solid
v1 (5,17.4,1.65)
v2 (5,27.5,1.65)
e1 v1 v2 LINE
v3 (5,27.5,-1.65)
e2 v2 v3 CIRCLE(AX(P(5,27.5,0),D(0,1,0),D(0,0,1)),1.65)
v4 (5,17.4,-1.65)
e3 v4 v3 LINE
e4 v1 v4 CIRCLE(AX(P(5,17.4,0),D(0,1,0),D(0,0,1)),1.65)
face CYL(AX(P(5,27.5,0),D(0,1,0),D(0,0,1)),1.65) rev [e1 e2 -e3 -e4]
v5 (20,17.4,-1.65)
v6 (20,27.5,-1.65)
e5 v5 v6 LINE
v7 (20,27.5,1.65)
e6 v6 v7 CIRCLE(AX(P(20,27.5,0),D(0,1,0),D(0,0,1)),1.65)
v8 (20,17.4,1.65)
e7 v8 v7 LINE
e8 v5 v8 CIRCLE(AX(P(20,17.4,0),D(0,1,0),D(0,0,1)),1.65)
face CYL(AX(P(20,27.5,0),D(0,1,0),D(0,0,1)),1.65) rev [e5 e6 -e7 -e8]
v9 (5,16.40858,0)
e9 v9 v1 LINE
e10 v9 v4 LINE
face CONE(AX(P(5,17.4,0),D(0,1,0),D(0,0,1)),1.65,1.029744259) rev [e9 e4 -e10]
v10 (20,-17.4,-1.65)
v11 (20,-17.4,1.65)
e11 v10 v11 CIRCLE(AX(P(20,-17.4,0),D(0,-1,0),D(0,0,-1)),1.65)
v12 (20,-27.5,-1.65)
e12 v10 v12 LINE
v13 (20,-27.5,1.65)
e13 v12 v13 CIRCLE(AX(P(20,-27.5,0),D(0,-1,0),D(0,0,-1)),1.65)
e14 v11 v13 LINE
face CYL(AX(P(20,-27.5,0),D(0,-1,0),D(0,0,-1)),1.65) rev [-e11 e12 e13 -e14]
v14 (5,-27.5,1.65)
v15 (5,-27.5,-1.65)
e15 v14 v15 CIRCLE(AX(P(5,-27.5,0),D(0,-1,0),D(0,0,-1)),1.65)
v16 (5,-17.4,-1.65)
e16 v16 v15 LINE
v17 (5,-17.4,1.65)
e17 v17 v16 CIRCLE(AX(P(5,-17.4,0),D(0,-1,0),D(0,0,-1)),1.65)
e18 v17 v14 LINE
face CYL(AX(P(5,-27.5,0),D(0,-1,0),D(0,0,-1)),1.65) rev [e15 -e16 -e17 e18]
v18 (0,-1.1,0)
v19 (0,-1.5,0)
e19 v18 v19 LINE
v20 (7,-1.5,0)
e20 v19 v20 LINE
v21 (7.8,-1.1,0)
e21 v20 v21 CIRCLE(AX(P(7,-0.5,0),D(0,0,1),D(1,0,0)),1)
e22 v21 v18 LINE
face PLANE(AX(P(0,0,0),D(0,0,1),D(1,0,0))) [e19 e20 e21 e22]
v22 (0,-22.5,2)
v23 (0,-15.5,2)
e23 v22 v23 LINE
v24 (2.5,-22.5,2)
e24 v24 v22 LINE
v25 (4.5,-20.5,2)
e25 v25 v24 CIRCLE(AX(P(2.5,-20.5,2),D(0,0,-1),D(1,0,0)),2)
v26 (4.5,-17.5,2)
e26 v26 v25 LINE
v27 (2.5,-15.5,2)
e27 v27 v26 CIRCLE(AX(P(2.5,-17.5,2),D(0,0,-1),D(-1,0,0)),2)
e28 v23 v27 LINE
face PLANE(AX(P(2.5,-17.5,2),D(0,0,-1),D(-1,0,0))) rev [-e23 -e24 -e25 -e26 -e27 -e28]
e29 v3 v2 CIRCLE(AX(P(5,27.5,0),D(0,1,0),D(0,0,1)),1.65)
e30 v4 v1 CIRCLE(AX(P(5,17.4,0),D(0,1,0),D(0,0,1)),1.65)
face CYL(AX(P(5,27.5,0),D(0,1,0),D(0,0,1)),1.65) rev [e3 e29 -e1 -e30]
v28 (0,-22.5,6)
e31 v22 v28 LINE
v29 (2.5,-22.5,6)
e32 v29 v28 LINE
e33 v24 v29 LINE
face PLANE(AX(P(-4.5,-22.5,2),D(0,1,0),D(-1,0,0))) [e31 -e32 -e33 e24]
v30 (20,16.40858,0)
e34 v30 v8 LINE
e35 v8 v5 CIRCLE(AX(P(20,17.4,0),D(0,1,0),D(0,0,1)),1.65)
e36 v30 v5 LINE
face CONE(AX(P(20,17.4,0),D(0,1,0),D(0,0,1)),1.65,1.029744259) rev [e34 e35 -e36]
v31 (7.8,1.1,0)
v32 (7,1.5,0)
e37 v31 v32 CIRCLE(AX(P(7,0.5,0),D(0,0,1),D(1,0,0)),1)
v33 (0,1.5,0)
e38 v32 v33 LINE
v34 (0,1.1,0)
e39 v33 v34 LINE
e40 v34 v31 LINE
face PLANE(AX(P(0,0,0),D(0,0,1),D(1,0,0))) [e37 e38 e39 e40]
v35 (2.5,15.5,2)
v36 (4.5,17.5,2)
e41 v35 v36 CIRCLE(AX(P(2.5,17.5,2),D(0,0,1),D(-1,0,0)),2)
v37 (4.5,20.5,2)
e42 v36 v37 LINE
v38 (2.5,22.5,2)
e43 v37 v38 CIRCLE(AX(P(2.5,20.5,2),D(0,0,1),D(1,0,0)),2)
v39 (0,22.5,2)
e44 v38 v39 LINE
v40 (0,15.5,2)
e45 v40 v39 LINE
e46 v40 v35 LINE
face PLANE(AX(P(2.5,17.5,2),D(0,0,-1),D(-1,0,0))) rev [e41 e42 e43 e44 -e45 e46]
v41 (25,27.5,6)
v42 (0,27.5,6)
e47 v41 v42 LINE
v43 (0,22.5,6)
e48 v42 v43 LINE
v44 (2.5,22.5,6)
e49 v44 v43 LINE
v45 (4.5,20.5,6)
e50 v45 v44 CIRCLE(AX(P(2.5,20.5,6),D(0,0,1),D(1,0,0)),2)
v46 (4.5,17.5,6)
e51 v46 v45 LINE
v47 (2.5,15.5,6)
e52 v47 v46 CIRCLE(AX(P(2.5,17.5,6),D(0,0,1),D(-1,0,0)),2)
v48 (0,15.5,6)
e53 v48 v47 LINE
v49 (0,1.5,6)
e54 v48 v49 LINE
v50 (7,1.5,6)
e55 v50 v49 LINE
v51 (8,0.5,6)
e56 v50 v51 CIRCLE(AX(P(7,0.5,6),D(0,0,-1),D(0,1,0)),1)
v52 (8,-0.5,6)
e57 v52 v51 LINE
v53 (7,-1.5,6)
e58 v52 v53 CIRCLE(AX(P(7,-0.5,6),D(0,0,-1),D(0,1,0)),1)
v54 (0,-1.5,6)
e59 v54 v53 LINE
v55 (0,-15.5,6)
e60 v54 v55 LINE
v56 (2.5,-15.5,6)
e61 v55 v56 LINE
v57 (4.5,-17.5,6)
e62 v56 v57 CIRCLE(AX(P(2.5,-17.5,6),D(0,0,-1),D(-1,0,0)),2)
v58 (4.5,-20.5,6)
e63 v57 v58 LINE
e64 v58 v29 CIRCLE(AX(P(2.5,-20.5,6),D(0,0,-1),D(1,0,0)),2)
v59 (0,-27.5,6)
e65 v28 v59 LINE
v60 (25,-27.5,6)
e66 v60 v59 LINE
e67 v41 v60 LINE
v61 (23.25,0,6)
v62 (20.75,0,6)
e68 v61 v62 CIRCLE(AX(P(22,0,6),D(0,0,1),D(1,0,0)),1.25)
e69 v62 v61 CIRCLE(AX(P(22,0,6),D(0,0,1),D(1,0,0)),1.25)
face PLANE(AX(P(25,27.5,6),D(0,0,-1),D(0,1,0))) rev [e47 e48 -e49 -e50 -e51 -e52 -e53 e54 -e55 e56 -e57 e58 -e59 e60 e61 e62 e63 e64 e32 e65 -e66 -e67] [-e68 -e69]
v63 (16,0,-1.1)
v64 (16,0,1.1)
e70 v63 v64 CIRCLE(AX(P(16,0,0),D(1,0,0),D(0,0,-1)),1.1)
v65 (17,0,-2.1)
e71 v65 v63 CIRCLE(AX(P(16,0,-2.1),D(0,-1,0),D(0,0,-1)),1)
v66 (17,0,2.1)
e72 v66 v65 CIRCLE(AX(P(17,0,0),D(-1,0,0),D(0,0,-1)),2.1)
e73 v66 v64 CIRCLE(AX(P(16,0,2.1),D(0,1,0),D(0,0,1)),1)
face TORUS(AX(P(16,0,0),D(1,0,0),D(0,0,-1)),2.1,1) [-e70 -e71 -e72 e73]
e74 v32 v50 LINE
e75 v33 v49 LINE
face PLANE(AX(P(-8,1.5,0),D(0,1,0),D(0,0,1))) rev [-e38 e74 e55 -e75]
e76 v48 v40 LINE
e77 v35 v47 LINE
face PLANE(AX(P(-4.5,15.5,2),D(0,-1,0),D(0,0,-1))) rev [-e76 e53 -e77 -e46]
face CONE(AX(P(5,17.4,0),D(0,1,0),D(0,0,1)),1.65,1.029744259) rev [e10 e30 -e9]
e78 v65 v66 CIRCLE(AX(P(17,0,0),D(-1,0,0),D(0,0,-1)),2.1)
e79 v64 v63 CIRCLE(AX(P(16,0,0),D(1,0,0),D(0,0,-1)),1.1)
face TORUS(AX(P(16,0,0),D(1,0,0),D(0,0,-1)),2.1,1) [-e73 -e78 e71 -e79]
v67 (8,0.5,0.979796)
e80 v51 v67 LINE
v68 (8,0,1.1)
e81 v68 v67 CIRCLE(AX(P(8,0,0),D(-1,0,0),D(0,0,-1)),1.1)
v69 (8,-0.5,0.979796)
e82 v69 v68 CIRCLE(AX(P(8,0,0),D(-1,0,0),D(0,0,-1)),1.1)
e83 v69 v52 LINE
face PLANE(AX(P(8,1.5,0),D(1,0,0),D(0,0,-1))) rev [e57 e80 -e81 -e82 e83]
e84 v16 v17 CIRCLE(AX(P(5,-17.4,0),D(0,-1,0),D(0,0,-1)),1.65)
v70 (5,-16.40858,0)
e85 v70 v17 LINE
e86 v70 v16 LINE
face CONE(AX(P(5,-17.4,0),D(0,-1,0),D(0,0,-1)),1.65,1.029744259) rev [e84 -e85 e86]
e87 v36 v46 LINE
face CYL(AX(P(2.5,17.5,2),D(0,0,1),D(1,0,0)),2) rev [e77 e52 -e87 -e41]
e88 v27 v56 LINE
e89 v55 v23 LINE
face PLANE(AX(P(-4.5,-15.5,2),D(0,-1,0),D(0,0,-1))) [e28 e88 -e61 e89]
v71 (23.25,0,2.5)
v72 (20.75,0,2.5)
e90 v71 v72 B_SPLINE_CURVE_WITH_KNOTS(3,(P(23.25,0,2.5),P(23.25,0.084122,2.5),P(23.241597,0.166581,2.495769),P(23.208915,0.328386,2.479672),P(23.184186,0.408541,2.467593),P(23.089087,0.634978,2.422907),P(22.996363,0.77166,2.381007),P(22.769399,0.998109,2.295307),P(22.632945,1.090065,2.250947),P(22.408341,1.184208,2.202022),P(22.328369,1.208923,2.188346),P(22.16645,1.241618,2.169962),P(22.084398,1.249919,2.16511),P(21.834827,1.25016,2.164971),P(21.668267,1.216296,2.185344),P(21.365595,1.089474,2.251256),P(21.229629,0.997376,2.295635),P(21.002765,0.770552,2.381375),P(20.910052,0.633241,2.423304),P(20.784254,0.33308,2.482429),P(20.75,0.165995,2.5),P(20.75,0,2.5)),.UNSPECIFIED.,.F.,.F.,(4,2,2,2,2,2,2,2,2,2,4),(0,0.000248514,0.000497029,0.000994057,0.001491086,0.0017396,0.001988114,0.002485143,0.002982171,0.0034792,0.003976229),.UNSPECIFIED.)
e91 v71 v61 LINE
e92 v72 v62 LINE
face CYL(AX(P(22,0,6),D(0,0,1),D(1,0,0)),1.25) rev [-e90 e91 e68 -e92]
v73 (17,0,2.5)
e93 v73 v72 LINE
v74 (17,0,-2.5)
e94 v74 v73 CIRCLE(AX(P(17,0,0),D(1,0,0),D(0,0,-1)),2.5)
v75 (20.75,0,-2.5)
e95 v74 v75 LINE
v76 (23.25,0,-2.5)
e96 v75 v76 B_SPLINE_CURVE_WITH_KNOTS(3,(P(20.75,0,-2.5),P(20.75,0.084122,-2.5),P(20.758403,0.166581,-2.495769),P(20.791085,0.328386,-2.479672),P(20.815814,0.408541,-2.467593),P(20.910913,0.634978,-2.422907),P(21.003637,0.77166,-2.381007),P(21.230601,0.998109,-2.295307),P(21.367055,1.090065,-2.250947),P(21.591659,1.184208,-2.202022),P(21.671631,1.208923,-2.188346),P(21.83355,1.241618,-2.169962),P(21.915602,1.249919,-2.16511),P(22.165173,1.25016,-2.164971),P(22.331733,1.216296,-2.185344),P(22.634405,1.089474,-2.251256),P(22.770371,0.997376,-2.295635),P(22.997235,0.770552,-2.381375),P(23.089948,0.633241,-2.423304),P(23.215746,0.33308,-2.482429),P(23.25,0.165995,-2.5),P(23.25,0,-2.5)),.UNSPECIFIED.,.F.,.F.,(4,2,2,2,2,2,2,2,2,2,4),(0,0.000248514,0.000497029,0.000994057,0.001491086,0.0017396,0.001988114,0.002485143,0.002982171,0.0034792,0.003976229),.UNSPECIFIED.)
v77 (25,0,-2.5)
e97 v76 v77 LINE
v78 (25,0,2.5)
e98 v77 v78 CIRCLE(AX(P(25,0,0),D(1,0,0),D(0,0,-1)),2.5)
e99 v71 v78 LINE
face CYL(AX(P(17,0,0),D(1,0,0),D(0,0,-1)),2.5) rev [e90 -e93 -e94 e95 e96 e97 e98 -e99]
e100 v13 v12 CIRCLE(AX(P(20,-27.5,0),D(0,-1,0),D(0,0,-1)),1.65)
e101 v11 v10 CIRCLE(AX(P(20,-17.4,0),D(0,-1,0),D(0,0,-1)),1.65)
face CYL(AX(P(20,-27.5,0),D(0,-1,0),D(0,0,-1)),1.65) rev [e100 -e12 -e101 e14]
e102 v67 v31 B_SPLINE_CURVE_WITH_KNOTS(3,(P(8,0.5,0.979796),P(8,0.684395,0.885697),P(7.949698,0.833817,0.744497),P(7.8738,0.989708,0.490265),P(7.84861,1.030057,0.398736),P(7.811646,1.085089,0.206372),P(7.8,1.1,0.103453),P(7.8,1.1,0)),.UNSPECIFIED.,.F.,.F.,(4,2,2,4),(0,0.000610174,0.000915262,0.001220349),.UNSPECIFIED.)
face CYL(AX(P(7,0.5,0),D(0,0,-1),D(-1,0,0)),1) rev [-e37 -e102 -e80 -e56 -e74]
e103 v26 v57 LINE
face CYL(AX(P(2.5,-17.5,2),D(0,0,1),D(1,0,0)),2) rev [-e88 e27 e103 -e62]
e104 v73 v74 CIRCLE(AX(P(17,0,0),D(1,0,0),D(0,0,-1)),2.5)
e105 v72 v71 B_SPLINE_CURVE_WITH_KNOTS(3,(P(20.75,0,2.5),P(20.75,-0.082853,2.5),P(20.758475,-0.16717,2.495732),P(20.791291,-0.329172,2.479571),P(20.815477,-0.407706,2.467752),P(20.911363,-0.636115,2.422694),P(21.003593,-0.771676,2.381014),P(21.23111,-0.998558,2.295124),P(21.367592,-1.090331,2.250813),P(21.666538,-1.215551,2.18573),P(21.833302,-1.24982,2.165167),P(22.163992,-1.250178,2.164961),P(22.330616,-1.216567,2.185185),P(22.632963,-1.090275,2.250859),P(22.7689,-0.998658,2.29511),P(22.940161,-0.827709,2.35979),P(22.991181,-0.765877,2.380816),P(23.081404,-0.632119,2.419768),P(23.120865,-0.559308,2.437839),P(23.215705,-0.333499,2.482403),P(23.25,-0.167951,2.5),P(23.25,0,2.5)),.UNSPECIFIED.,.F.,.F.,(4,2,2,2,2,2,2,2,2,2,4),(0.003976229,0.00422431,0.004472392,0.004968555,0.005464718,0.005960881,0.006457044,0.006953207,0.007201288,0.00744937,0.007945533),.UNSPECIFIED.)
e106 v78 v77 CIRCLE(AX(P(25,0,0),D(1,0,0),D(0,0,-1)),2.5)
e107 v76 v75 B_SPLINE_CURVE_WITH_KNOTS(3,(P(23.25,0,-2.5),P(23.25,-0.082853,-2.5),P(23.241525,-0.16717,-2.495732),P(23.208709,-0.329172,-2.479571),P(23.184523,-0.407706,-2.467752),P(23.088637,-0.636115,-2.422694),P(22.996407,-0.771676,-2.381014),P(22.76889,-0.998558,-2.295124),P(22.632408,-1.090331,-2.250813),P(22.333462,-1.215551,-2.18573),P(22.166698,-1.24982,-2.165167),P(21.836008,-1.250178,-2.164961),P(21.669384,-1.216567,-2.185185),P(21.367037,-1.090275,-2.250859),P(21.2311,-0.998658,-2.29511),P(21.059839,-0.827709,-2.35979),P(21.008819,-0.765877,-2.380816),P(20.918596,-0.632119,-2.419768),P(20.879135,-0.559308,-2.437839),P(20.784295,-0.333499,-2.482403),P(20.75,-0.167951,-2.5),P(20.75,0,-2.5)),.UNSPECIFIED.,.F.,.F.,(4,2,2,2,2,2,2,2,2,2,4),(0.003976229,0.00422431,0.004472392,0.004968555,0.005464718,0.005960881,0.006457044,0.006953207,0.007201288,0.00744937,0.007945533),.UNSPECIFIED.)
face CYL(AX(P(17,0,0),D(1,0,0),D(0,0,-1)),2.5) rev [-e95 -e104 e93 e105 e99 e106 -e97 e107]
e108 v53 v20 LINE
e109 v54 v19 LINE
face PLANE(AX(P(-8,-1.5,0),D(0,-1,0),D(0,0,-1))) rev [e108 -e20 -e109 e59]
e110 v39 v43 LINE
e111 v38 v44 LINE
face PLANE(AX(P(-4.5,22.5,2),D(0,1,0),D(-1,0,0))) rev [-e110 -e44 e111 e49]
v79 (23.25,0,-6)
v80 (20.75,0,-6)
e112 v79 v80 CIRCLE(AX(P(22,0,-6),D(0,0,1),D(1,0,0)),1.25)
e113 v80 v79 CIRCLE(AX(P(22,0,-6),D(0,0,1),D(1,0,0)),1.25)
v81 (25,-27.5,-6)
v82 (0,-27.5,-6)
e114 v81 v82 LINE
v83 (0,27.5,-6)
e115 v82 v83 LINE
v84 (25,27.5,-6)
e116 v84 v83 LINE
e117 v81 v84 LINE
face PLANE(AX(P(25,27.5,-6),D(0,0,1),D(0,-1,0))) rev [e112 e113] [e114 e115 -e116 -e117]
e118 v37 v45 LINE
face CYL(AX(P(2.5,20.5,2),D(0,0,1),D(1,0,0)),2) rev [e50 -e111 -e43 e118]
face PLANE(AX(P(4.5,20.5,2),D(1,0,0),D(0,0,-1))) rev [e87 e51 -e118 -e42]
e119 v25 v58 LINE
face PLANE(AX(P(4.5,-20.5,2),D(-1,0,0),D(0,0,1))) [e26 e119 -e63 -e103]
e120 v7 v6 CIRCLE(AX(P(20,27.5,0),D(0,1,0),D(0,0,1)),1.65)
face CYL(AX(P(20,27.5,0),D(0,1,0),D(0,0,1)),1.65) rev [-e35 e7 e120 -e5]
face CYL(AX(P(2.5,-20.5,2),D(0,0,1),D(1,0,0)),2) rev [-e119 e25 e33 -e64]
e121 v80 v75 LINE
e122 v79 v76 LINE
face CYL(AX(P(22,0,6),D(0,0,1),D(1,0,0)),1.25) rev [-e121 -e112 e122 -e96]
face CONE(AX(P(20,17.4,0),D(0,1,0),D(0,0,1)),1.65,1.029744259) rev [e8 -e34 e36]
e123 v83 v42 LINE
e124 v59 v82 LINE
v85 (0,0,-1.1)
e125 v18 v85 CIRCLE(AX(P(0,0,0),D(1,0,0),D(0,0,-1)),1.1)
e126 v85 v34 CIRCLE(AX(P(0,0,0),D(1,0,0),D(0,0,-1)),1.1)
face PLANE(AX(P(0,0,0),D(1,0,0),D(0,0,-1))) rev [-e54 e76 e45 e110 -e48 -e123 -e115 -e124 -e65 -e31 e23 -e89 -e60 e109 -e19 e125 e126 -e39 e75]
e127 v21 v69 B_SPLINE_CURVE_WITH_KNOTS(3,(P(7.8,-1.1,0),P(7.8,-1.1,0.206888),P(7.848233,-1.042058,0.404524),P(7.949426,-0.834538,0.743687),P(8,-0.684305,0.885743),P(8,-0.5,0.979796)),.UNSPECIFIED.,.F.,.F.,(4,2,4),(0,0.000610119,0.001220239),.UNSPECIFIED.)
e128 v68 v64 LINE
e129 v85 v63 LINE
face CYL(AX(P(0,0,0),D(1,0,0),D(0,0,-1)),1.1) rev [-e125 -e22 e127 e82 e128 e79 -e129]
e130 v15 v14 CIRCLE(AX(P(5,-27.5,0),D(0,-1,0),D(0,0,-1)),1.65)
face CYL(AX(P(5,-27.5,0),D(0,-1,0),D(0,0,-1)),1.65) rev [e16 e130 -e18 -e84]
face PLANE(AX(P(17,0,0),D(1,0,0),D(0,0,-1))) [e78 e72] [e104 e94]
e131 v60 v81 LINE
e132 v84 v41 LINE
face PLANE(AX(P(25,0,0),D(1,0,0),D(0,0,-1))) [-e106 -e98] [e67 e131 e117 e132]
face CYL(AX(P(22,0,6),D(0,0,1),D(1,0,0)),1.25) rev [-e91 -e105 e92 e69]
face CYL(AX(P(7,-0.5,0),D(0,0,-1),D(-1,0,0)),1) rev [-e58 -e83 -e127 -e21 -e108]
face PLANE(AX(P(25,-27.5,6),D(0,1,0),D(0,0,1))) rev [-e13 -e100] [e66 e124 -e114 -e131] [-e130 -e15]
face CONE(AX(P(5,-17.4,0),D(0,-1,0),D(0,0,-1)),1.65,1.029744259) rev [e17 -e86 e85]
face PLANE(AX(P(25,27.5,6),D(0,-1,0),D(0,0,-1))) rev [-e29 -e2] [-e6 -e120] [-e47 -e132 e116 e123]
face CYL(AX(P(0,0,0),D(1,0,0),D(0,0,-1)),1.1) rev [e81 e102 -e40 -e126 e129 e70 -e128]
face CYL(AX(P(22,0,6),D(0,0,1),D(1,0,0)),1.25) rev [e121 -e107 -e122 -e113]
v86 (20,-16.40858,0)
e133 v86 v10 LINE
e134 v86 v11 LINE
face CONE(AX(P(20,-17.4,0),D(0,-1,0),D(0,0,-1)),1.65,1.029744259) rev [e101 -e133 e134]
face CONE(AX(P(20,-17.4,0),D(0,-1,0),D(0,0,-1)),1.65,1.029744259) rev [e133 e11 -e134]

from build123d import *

# Parameters (mm, degrees)
SKETCH_1_W                  = 12
SKETCH_1_H                  = 55
EXTRUDE_1_DEPTH             = 25
SKETCH_2_R                  = 1.1
CUT_EXTRUDE_1_DEPTH         = 25
SKETCH_3_R                  = 2.5
CUT_EXTRUDE_2_DEPTH         = 8
SKETCH_4_W                  = 16
SKETCH_4_H                  = 3
CUT_EXTRUDE_3_DEPTH         = 6
HOLE_WIZARD_M4_1_AT_2_COUNT = 2
HOLE_WIZARD_M4_1_AT_2_PITCH = 15
FILLET_1_R                  = 1
CUT_EXTRUDE_4_DEPTH         = 4
HOLE_WIZARD_M3_1_D          = 2.5
FILLET_2_R                  = 1


with BuildPart() as part:
    # 草图1 → 凸台-拉伸1 (new body)
    with BuildSketch(Plane(origin=(0, 0, 0), x_dir=(0, 0, -1), z_dir=(1, 0, 0))):
        Rectangle(SKETCH_1_W, SKETCH_1_H)
    extrude(amount=EXTRUDE_1_DEPTH)

    # 草图2 → 切除-拉伸1 (cut)
    with BuildSketch(Plane(origin=(25, 0, 0), x_dir=(0, 0, -1), z_dir=(1, 0, 0))):
        Circle(SKETCH_2_R)
    extrude(amount=-CUT_EXTRUDE_1_DEPTH, mode=Mode.SUBTRACT)

    # 草图3 → 切除-拉伸2 (cut)
    with BuildSketch(Plane(origin=(25, 0, 0), x_dir=(0, 0, -1), z_dir=(1, 0, 0))):
        Circle(SKETCH_3_R)
    extrude(amount=-CUT_EXTRUDE_2_DEPTH, mode=Mode.SUBTRACT)

    # 草图4 → 切除-拉伸3 (cut)
    with BuildSketch(Plane.XY.offset(6)):
        Rectangle(SKETCH_4_W, SKETCH_4_H)
    extrude(amount=-CUT_EXTRUDE_3_DEPTH, mode=Mode.SUBTRACT)

    # 草图7 → M4 螺纹孔1 (revolve, cut)
    with BuildSketch(Plane(origin=(5, 27.5, 0), x_dir=(0, 0, 1), z_dir=(1, 0, 0))):
        Polygon((0, 0), (0, 11.091420021), (1.65, 10.1), (1.65, 0), align=None)
    hole_wizard_m4_1 = revolve(axis=Axis((5, 33.85, 0), (0, -1, 0)), mode=Mode.SUBTRACT)

    # M4 螺纹孔1 at 2: M4 螺纹孔1 ×2
    with Locations(*[(i * HOLE_WIZARD_M4_1_AT_2_PITCH, 0, 0) for i in range(1, HOLE_WIZARD_M4_1_AT_2_COUNT)]):
        add(hole_wizard_m4_1, mode=Mode.SUBTRACT)

    # 镜向1: M4 螺纹孔1 across plane
    add(hole_wizard_m4_1.mirror(Plane.ZX), mode=Mode.SUBTRACT)

    # 镜向1 copy 1 sketch → 镜向1 copy 1 (revolve, cut)
    with BuildSketch(Plane(origin=(20, -27.5, 0), x_dir=(0, 0, 1), z_dir=(1, 0, 0))):
        Polygon((0, 0), (0, -11.091420021), (1.65, -10.1), (1.65, 0), align=None)
    revolve(axis=Axis((20, -33.85, 0), (0, -1, 0)), mode=Mode.SUBTRACT)

    # 圆角1
    fillet_1_edges = [part.edges().sort_by_distance(p)[0] for p in [
        (8, -1.5, 3),
        (8, 1.5, 3),
    ]]
    fillet(fillet_1_edges, radius=FILLET_1_R)

    # 草图9 → 切除-拉伸4 (cut)
    with BuildSketch(Plane.XY.offset(6)):
        with BuildLine():
            Line((-4.5, 22.5), (2.5, 22.5))
            ThreePointArc((2.5, 22.5), (3.914213562, 21.914213562), (4.5, 20.5))
            Line((4.5, 20.5), (4.5, 17.5))
            ThreePointArc((4.5, 17.5), (3.914213562, 16.085786438), (2.5, 15.5))
            Line((2.5, 15.5), (-4.5, 15.5))
            Line((-4.5, 15.5), (-4.5, 22.5))
        make_face()
    cut_extrude_4 = extrude(amount=-CUT_EXTRUDE_4_DEPTH, mode=Mode.SUBTRACT)

    # 镜向2: 切除-拉伸4 across plane
    add(cut_extrude_4.mirror(Plane.ZX), mode=Mode.SUBTRACT)

    # M3 螺纹孔1 (through all)
    with Locations(Plane.XY.offset(6)):
        with Locations((22, 0)):
            Hole(HOLE_WIZARD_M3_1_D / 2)

    # 圆角2
    fillet_2_edges = [part.edges().sort_by_distance(p)[0] for p in [
        (17, 0, 1.1),
    ]]
    fillet(fillet_2_edges, radius=FILLET_2_R)


solid = part.part
